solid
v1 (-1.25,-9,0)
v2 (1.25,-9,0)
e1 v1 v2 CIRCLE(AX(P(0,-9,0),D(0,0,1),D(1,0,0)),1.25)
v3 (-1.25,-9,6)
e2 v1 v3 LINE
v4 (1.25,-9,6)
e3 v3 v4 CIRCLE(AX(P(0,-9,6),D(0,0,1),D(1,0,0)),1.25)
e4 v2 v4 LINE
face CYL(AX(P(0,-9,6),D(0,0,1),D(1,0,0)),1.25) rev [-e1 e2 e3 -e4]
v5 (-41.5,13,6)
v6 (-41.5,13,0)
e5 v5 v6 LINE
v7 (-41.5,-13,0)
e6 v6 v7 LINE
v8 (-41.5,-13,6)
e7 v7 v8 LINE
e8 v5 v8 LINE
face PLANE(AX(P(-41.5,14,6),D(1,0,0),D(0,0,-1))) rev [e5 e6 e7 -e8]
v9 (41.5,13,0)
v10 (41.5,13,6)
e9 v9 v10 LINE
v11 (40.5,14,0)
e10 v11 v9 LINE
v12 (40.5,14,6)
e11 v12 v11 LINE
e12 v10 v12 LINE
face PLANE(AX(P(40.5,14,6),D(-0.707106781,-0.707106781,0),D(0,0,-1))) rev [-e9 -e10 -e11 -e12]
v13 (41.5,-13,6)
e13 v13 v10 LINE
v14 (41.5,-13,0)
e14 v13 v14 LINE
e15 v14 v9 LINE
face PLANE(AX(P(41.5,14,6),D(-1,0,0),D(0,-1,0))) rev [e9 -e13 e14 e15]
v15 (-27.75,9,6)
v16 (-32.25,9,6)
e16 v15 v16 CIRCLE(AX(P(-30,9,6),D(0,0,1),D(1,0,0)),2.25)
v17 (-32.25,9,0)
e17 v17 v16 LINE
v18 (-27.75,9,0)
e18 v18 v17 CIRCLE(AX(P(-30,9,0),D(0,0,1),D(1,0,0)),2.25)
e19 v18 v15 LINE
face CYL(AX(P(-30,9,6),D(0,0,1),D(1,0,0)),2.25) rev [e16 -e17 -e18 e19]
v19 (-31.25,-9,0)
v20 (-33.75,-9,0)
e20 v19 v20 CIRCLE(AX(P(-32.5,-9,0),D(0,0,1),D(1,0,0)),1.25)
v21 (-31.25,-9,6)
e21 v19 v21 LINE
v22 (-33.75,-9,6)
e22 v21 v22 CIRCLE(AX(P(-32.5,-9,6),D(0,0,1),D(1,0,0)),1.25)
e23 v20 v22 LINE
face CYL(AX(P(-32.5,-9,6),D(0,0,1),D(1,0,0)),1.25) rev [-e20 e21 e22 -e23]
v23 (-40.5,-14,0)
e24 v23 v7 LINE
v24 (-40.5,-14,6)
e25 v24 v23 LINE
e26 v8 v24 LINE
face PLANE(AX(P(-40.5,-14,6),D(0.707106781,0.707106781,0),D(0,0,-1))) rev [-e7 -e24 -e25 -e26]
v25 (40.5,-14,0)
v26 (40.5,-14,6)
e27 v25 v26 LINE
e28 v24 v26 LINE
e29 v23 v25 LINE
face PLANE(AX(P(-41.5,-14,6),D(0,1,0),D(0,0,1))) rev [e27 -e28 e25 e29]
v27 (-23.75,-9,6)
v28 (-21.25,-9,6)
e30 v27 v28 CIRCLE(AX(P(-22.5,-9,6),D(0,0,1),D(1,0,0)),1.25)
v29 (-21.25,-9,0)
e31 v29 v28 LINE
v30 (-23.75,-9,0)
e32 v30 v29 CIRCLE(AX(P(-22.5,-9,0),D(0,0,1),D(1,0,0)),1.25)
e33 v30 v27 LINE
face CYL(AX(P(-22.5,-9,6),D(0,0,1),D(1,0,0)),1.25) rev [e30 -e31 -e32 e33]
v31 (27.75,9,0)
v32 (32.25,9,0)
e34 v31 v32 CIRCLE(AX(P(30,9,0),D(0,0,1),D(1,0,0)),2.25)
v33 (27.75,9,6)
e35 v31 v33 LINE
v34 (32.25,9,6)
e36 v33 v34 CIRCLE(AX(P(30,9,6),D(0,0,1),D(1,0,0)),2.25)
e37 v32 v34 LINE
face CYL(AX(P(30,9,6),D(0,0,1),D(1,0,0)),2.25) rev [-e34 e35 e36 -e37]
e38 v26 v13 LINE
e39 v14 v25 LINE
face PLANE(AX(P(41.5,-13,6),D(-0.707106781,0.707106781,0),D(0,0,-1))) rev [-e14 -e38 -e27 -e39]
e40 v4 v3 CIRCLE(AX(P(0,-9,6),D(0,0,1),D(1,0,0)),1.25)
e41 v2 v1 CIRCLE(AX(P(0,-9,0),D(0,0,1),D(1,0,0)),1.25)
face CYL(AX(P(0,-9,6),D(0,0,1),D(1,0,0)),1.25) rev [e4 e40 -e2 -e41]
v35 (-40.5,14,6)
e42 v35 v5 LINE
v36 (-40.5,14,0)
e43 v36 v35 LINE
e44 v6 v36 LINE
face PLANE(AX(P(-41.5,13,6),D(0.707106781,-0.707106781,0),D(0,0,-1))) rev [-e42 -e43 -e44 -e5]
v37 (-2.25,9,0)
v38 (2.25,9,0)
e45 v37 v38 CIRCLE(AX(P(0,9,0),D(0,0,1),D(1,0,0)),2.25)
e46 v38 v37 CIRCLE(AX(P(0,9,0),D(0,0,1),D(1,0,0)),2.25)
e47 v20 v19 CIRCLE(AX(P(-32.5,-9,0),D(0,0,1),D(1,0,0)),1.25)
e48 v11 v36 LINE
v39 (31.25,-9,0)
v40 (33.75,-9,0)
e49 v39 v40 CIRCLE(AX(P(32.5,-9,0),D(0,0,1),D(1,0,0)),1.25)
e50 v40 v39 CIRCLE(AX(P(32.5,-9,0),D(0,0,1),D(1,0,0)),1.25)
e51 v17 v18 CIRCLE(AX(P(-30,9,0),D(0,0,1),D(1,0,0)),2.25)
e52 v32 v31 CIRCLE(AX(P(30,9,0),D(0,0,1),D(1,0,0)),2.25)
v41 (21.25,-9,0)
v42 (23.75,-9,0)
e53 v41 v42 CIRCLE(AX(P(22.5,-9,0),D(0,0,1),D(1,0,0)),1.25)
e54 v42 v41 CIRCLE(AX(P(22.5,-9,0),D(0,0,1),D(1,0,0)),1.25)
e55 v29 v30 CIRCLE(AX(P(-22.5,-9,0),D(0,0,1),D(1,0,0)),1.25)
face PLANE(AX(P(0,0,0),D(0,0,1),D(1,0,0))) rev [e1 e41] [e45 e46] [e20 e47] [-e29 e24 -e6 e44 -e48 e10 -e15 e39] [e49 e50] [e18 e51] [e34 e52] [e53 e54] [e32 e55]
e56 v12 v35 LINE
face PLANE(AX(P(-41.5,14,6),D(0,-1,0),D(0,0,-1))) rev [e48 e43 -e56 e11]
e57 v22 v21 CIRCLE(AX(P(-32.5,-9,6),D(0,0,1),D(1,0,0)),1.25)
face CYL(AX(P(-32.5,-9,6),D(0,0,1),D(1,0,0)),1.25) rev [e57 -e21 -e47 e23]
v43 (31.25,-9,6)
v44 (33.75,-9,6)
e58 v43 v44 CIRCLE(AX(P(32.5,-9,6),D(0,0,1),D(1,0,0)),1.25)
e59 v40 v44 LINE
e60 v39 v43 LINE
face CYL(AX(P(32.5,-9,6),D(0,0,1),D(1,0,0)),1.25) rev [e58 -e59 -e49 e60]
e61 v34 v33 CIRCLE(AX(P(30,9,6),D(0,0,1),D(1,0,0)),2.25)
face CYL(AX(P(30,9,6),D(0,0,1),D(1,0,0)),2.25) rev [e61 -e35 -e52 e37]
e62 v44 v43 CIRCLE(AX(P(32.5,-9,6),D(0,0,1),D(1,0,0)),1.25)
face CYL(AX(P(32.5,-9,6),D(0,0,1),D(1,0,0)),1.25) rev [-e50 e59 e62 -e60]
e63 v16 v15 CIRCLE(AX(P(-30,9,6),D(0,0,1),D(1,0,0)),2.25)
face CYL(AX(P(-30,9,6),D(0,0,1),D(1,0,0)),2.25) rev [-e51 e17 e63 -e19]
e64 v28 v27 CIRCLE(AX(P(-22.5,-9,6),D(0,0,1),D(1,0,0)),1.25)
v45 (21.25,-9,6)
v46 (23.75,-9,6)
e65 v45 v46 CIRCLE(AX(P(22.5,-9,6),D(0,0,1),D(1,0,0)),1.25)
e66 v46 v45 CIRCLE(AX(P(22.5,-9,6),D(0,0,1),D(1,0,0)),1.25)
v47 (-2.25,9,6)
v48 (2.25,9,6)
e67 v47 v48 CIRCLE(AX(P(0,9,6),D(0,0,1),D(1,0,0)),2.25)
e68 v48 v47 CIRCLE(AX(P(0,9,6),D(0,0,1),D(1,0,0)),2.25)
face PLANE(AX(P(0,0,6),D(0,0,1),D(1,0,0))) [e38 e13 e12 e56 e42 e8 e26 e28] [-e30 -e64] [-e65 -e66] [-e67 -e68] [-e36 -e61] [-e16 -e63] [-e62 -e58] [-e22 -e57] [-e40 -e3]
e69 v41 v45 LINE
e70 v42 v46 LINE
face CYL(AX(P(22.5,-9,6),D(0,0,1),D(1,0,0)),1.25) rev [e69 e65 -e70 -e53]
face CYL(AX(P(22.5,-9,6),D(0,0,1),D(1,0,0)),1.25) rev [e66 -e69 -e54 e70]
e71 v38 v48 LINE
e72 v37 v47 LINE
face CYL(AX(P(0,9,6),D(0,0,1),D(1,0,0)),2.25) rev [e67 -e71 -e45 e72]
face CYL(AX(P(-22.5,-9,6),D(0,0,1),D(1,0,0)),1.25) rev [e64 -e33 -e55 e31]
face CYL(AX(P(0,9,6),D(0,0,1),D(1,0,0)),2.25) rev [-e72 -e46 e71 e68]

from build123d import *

# Parameters (mm, degrees)
SKETCH_1_W         = 83
SKETCH_1_H         = 28
EXTRUDE_1_DEPTH    = 6
HOLE_WIZARD_M4_1_D = 4.5
HOLE_WIZARD_M3_1_D = 2.5
CHAMFER_1_SIZE     = 1


with BuildPart() as part:
    # 草图1 → 凸台-拉伸1 (new body)
    with BuildSketch(Plane.XY):
        Rectangle(SKETCH_1_W, SKETCH_1_H)
    extrude(amount=EXTRUDE_1_DEPTH)

    # M4 间隙孔1 (through all)
    with Locations(Plane.XY.offset(6)):
        with Locations((-30, 9), (0, 9), (30, 9)):
            Hole(HOLE_WIZARD_M4_1_D / 2)

    # M3 螺纹孔1 (through all)
    with Locations(Plane.XY.offset(6)):
        with Locations((-32.5, -9), (0, -9), (32.5, -9), (22.5, -9), (-22.5, -9)):
            Hole(HOLE_WIZARD_M3_1_D / 2)

    # 倒角1
    chamfer_1_edges = [part.edges().sort_by_distance(p)[0] for p in [
        (41.5, -14, 3),
        (-41.5, -14, 3),
        (-41.5, 14, 3),
        (41.5, 14, 3),
    ]]
    chamfer(chamfer_1_edges, length=CHAMFER_1_SIZE)


solid = part.part
